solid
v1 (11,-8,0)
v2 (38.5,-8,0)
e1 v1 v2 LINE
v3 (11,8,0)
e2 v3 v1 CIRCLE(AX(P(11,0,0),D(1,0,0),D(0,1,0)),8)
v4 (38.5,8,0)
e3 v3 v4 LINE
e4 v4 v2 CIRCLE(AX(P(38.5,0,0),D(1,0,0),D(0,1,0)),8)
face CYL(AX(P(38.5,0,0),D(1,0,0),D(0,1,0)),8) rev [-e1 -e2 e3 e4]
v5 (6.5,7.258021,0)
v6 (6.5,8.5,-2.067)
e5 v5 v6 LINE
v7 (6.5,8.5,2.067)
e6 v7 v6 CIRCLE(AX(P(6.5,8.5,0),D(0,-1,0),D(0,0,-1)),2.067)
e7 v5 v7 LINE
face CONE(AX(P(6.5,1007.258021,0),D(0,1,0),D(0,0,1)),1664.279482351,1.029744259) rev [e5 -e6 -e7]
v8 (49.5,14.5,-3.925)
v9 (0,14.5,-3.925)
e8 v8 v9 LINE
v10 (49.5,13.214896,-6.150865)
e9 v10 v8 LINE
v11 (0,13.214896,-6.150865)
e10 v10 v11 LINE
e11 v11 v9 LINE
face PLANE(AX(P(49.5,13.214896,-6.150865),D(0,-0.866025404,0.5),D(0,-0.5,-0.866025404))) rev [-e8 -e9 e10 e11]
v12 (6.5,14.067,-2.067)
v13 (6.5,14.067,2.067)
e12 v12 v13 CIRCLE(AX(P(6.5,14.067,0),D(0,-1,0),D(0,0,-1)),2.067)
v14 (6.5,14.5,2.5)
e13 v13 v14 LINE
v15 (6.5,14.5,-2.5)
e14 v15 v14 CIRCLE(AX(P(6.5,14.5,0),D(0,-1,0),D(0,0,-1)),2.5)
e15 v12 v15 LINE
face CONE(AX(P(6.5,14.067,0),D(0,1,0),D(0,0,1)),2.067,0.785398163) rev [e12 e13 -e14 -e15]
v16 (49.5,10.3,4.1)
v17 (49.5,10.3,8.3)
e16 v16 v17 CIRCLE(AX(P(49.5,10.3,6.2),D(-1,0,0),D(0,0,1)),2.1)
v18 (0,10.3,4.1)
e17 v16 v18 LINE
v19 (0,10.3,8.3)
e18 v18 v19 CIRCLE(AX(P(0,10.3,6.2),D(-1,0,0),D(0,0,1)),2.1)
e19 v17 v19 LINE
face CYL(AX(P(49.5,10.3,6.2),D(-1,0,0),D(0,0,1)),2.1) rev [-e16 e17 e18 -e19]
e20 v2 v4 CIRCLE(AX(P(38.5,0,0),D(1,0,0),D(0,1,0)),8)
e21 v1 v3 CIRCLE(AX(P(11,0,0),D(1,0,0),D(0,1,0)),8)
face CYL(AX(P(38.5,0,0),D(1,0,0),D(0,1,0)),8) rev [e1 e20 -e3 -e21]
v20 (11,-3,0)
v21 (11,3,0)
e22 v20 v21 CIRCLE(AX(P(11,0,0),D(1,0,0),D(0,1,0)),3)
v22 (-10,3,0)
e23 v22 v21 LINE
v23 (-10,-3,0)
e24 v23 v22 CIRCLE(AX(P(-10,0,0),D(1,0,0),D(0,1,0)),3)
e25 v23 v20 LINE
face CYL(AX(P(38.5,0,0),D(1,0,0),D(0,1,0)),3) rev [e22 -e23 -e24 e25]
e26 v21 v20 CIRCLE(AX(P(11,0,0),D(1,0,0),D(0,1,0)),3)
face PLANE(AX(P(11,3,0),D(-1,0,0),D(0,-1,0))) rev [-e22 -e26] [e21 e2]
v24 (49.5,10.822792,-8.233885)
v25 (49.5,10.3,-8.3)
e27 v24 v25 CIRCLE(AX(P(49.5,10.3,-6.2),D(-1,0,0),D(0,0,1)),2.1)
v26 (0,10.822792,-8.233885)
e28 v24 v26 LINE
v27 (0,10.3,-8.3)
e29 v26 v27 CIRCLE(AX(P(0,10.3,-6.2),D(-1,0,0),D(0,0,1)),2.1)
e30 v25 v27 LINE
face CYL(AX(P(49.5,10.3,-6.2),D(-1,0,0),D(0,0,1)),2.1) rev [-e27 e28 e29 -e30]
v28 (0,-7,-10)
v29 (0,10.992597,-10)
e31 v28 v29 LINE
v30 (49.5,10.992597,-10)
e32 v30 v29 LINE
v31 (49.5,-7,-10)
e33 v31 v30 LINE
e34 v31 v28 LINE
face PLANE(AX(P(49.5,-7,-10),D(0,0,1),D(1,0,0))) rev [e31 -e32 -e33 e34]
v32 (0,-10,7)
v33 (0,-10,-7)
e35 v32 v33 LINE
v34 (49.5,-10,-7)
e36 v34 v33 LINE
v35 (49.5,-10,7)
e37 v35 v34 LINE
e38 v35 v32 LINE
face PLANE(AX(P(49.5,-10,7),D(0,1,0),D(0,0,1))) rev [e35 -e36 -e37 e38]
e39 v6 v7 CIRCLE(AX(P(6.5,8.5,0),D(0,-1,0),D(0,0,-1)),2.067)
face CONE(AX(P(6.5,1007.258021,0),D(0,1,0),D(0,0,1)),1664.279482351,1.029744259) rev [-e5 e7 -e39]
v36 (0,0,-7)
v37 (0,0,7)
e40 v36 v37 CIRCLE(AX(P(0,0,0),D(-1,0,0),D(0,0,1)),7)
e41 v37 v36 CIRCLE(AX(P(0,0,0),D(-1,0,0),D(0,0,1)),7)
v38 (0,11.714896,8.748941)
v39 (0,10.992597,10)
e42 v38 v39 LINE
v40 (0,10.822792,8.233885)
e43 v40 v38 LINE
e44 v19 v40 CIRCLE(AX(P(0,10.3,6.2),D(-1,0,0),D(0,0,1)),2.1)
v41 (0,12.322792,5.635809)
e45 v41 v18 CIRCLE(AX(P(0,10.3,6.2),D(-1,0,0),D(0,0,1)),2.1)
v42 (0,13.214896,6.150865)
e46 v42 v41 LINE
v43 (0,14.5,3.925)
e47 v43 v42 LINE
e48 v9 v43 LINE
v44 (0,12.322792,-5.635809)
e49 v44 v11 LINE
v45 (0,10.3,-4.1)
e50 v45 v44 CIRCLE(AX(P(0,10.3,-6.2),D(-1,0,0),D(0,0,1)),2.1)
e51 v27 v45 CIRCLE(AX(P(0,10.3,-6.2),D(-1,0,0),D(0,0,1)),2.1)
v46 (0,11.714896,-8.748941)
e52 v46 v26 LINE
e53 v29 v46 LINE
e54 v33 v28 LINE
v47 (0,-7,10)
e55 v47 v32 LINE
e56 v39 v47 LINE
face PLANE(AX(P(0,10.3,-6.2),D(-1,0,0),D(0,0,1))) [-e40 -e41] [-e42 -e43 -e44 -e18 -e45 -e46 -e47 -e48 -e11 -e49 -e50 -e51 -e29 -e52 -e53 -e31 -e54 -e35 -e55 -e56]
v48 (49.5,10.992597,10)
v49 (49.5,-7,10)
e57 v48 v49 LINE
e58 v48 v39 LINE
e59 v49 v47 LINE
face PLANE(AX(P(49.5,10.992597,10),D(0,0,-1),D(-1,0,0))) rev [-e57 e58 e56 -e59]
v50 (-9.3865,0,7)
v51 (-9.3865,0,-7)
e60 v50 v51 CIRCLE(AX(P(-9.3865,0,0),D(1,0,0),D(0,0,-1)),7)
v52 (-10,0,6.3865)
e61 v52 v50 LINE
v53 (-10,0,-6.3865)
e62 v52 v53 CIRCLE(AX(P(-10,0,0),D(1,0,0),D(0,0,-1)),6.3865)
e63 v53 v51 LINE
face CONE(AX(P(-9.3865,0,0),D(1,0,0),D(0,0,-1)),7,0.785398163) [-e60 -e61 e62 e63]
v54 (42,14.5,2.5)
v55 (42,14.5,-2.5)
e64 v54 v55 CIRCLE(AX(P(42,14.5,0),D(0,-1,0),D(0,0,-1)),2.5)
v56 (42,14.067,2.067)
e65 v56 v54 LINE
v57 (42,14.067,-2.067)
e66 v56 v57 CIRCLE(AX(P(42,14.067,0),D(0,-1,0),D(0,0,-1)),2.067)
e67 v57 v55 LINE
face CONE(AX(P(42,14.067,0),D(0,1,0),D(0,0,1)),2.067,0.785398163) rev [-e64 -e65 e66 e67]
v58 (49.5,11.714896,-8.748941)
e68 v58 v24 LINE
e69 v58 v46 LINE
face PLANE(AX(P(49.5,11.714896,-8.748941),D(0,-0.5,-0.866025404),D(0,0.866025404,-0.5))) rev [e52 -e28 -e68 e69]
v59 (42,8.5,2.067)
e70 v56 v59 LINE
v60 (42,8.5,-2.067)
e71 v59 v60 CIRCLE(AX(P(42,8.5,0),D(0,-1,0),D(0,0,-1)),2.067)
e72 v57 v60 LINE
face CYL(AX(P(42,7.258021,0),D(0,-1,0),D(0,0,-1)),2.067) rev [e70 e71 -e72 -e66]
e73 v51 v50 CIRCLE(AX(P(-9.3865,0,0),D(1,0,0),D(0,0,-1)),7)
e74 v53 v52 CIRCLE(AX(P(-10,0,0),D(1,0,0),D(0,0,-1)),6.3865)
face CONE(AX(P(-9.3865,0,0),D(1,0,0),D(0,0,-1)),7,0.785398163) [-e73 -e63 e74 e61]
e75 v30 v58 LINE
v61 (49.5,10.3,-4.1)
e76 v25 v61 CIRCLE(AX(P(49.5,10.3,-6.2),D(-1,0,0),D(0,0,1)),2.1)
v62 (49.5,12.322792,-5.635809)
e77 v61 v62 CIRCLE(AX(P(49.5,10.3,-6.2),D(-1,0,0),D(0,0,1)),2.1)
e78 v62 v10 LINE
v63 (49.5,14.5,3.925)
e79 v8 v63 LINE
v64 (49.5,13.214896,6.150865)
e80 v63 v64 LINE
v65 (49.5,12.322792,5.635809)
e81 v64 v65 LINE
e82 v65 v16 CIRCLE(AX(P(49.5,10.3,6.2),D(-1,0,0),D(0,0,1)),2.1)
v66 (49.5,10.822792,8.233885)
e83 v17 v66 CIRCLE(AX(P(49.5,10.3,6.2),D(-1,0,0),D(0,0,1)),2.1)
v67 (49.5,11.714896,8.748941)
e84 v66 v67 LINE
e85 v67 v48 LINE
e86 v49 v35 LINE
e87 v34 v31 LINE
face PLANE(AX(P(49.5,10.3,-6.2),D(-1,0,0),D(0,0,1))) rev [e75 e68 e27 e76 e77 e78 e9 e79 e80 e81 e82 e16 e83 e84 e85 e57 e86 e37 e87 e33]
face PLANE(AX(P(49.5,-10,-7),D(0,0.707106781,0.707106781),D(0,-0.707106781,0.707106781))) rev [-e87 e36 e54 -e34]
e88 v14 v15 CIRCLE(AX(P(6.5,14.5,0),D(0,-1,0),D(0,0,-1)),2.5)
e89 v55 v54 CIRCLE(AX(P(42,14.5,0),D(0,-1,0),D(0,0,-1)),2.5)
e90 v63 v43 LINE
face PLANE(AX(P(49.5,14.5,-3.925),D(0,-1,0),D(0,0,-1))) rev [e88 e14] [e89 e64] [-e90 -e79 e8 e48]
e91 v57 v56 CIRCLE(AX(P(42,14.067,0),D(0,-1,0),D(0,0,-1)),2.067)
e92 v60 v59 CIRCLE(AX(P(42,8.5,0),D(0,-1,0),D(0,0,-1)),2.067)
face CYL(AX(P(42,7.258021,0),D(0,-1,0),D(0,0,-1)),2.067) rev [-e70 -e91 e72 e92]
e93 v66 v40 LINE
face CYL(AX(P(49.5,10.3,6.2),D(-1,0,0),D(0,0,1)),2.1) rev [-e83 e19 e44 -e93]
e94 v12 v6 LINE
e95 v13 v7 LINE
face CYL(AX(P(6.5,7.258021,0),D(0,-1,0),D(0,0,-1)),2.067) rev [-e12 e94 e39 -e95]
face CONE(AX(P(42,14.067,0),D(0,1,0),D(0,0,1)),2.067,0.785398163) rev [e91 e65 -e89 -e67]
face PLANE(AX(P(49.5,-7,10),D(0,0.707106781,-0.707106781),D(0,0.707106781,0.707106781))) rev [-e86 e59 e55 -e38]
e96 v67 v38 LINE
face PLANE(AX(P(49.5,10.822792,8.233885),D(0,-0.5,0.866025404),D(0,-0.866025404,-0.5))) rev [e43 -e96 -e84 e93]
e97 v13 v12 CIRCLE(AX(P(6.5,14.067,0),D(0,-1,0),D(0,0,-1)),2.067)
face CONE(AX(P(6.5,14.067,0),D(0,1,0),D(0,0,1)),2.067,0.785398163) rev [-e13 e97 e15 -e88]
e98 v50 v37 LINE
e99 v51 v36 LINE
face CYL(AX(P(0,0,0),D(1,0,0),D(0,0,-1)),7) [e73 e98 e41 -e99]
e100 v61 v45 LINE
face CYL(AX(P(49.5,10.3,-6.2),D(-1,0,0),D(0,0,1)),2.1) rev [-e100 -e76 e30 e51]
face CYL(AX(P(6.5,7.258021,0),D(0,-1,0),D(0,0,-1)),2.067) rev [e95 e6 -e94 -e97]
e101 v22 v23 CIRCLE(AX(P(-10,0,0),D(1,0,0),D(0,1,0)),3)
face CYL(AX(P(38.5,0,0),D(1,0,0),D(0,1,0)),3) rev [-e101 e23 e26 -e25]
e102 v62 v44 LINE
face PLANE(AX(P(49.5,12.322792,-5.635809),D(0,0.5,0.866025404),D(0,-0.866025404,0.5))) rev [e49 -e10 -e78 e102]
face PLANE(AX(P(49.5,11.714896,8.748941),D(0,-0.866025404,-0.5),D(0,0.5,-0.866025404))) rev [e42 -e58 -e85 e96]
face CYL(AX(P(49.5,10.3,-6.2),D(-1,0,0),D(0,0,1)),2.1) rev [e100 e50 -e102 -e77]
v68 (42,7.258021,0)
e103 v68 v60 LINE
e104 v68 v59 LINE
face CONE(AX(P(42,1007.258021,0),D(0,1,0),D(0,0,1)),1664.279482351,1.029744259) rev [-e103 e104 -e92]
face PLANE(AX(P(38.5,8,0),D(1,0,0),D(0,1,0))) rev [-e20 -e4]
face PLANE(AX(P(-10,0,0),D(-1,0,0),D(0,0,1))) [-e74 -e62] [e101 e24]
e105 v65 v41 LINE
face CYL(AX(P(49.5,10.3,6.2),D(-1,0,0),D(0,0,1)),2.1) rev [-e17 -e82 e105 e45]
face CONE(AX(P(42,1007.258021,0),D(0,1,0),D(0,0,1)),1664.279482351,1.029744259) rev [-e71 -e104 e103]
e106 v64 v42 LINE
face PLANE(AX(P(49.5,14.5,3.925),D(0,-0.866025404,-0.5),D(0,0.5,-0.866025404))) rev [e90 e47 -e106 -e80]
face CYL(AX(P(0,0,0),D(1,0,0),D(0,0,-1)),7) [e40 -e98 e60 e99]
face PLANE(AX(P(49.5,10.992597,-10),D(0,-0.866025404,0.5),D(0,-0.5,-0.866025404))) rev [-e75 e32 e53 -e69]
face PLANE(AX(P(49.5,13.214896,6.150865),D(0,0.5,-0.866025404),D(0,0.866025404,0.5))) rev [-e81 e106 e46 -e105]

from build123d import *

# Parameters (mm, degrees)
BOSS_EXTRUDE1_DEPTH = 49.5


with BuildPart() as part:
    # Sketch1 → Boss-Extrude1 (new body)
    with BuildSketch(Plane(origin=(0, 0, 0), x_dir=(0, 0, -1), z_dir=(1, 0, 0))):
        with BuildLine():
            Line((-10, -7), (-7, -10))
            Line((-7, -10), (7, -10))
            Line((7, -10), (10, -7))
            Line((10, -7), (10, 10.992597115))
            Line((10, 10.992597115), (8.748941454, 11.714896103))
            Line((8.748941454, 11.714896103), (8.233885029, 10.822792206))
            ThreePointArc((8.233885029, 10.822792206), (5.15, 8.481346652), (5.635808817, 12.322792206))
            Line((5.635808817, 12.322792206), (6.150865242, 13.214896103))
            Line((6.150865242, 13.214896103), (3.925, 14.5))
            Line((3.925, 14.5), (-3.925, 14.5))
            Line((-3.925, 14.5), (-6.150865242, 13.214896103))
            Line((-6.150865242, 13.214896103), (-5.635808817, 12.322792206))
            ThreePointArc((-5.635808817, 12.322792206), (-5.15, 8.481346652), (-8.233885029, 10.822792206))
            Line((-8.233885029, 10.822792206), (-8.748941454, 11.714896103))
            Line((-8.748941454, 11.714896103), (-10, 10.992597115))
            Line((-10, 10.992597115), (-10, -7))
        make_face()
    extrude(amount=BOSS_EXTRUDE1_DEPTH)

    # Sketch2 → Revolve1 (revolve)
    with BuildSketch(Plane.XY, mode=Mode.PRIVATE) as revolve1_sk:
        Polygon((-10, 0), (-10, 6.3865), (-9.3865, 7), (0, 7), (0, 0), align=None)
    revolve(revolve1_sk.sketch.rotate(Axis((0, 0, 0), (-1, 0, 0)), 90), axis=Axis((0, 0, 0), (-1, 0, 0)))

    # Sketch3 → Cut-Revolve1 (revolve, cut)
    with BuildSketch(Plane.XY):
        Polygon((-10, 0), (-10, 3), (11, 3), (11, 8), (38.5, 8), (38.5, 0), align=None)
    revolve(axis=Axis((38.5, 0, 0), (-1, 0, 0)), mode=Mode.SUBTRACT)

    # Sketch4 → Cut-Revolve2 (revolve, cut)
    with BuildSketch(Plane.XY, mode=Mode.PRIVATE) as cut_revolve2_sk:
        Polygon((6.5, 14.5), (9, 14.5), (8.567, 14.067), (8.567, 8.5), (6.5, 7.2580211), align=None)
    revolve(cut_revolve2_sk.sketch.rotate(Axis((6.5, 7.2580211, 0), (0, 1, 0)), 90), axis=Axis((6.5, 7.2580211, 0), (0, 1, 0)), mode=Mode.SUBTRACT)

    # Sketch5 → Cut-Revolve3 (revolve, cut)
    with BuildSketch(Plane.XY, mode=Mode.PRIVATE) as cut_revolve3_sk:
        Polygon((42, 14.5), (44.5, 14.5), (44.067, 14.067), (44.067, 8.5), (42, 7.2580211), align=None)
    revolve(cut_revolve3_sk.sketch.rotate(Axis((42, 7.2580211, 0), (0, 1, 0)), 90), axis=Axis((42, 7.2580211, 0), (0, 1, 0)), mode=Mode.SUBTRACT)


solid = part.part
